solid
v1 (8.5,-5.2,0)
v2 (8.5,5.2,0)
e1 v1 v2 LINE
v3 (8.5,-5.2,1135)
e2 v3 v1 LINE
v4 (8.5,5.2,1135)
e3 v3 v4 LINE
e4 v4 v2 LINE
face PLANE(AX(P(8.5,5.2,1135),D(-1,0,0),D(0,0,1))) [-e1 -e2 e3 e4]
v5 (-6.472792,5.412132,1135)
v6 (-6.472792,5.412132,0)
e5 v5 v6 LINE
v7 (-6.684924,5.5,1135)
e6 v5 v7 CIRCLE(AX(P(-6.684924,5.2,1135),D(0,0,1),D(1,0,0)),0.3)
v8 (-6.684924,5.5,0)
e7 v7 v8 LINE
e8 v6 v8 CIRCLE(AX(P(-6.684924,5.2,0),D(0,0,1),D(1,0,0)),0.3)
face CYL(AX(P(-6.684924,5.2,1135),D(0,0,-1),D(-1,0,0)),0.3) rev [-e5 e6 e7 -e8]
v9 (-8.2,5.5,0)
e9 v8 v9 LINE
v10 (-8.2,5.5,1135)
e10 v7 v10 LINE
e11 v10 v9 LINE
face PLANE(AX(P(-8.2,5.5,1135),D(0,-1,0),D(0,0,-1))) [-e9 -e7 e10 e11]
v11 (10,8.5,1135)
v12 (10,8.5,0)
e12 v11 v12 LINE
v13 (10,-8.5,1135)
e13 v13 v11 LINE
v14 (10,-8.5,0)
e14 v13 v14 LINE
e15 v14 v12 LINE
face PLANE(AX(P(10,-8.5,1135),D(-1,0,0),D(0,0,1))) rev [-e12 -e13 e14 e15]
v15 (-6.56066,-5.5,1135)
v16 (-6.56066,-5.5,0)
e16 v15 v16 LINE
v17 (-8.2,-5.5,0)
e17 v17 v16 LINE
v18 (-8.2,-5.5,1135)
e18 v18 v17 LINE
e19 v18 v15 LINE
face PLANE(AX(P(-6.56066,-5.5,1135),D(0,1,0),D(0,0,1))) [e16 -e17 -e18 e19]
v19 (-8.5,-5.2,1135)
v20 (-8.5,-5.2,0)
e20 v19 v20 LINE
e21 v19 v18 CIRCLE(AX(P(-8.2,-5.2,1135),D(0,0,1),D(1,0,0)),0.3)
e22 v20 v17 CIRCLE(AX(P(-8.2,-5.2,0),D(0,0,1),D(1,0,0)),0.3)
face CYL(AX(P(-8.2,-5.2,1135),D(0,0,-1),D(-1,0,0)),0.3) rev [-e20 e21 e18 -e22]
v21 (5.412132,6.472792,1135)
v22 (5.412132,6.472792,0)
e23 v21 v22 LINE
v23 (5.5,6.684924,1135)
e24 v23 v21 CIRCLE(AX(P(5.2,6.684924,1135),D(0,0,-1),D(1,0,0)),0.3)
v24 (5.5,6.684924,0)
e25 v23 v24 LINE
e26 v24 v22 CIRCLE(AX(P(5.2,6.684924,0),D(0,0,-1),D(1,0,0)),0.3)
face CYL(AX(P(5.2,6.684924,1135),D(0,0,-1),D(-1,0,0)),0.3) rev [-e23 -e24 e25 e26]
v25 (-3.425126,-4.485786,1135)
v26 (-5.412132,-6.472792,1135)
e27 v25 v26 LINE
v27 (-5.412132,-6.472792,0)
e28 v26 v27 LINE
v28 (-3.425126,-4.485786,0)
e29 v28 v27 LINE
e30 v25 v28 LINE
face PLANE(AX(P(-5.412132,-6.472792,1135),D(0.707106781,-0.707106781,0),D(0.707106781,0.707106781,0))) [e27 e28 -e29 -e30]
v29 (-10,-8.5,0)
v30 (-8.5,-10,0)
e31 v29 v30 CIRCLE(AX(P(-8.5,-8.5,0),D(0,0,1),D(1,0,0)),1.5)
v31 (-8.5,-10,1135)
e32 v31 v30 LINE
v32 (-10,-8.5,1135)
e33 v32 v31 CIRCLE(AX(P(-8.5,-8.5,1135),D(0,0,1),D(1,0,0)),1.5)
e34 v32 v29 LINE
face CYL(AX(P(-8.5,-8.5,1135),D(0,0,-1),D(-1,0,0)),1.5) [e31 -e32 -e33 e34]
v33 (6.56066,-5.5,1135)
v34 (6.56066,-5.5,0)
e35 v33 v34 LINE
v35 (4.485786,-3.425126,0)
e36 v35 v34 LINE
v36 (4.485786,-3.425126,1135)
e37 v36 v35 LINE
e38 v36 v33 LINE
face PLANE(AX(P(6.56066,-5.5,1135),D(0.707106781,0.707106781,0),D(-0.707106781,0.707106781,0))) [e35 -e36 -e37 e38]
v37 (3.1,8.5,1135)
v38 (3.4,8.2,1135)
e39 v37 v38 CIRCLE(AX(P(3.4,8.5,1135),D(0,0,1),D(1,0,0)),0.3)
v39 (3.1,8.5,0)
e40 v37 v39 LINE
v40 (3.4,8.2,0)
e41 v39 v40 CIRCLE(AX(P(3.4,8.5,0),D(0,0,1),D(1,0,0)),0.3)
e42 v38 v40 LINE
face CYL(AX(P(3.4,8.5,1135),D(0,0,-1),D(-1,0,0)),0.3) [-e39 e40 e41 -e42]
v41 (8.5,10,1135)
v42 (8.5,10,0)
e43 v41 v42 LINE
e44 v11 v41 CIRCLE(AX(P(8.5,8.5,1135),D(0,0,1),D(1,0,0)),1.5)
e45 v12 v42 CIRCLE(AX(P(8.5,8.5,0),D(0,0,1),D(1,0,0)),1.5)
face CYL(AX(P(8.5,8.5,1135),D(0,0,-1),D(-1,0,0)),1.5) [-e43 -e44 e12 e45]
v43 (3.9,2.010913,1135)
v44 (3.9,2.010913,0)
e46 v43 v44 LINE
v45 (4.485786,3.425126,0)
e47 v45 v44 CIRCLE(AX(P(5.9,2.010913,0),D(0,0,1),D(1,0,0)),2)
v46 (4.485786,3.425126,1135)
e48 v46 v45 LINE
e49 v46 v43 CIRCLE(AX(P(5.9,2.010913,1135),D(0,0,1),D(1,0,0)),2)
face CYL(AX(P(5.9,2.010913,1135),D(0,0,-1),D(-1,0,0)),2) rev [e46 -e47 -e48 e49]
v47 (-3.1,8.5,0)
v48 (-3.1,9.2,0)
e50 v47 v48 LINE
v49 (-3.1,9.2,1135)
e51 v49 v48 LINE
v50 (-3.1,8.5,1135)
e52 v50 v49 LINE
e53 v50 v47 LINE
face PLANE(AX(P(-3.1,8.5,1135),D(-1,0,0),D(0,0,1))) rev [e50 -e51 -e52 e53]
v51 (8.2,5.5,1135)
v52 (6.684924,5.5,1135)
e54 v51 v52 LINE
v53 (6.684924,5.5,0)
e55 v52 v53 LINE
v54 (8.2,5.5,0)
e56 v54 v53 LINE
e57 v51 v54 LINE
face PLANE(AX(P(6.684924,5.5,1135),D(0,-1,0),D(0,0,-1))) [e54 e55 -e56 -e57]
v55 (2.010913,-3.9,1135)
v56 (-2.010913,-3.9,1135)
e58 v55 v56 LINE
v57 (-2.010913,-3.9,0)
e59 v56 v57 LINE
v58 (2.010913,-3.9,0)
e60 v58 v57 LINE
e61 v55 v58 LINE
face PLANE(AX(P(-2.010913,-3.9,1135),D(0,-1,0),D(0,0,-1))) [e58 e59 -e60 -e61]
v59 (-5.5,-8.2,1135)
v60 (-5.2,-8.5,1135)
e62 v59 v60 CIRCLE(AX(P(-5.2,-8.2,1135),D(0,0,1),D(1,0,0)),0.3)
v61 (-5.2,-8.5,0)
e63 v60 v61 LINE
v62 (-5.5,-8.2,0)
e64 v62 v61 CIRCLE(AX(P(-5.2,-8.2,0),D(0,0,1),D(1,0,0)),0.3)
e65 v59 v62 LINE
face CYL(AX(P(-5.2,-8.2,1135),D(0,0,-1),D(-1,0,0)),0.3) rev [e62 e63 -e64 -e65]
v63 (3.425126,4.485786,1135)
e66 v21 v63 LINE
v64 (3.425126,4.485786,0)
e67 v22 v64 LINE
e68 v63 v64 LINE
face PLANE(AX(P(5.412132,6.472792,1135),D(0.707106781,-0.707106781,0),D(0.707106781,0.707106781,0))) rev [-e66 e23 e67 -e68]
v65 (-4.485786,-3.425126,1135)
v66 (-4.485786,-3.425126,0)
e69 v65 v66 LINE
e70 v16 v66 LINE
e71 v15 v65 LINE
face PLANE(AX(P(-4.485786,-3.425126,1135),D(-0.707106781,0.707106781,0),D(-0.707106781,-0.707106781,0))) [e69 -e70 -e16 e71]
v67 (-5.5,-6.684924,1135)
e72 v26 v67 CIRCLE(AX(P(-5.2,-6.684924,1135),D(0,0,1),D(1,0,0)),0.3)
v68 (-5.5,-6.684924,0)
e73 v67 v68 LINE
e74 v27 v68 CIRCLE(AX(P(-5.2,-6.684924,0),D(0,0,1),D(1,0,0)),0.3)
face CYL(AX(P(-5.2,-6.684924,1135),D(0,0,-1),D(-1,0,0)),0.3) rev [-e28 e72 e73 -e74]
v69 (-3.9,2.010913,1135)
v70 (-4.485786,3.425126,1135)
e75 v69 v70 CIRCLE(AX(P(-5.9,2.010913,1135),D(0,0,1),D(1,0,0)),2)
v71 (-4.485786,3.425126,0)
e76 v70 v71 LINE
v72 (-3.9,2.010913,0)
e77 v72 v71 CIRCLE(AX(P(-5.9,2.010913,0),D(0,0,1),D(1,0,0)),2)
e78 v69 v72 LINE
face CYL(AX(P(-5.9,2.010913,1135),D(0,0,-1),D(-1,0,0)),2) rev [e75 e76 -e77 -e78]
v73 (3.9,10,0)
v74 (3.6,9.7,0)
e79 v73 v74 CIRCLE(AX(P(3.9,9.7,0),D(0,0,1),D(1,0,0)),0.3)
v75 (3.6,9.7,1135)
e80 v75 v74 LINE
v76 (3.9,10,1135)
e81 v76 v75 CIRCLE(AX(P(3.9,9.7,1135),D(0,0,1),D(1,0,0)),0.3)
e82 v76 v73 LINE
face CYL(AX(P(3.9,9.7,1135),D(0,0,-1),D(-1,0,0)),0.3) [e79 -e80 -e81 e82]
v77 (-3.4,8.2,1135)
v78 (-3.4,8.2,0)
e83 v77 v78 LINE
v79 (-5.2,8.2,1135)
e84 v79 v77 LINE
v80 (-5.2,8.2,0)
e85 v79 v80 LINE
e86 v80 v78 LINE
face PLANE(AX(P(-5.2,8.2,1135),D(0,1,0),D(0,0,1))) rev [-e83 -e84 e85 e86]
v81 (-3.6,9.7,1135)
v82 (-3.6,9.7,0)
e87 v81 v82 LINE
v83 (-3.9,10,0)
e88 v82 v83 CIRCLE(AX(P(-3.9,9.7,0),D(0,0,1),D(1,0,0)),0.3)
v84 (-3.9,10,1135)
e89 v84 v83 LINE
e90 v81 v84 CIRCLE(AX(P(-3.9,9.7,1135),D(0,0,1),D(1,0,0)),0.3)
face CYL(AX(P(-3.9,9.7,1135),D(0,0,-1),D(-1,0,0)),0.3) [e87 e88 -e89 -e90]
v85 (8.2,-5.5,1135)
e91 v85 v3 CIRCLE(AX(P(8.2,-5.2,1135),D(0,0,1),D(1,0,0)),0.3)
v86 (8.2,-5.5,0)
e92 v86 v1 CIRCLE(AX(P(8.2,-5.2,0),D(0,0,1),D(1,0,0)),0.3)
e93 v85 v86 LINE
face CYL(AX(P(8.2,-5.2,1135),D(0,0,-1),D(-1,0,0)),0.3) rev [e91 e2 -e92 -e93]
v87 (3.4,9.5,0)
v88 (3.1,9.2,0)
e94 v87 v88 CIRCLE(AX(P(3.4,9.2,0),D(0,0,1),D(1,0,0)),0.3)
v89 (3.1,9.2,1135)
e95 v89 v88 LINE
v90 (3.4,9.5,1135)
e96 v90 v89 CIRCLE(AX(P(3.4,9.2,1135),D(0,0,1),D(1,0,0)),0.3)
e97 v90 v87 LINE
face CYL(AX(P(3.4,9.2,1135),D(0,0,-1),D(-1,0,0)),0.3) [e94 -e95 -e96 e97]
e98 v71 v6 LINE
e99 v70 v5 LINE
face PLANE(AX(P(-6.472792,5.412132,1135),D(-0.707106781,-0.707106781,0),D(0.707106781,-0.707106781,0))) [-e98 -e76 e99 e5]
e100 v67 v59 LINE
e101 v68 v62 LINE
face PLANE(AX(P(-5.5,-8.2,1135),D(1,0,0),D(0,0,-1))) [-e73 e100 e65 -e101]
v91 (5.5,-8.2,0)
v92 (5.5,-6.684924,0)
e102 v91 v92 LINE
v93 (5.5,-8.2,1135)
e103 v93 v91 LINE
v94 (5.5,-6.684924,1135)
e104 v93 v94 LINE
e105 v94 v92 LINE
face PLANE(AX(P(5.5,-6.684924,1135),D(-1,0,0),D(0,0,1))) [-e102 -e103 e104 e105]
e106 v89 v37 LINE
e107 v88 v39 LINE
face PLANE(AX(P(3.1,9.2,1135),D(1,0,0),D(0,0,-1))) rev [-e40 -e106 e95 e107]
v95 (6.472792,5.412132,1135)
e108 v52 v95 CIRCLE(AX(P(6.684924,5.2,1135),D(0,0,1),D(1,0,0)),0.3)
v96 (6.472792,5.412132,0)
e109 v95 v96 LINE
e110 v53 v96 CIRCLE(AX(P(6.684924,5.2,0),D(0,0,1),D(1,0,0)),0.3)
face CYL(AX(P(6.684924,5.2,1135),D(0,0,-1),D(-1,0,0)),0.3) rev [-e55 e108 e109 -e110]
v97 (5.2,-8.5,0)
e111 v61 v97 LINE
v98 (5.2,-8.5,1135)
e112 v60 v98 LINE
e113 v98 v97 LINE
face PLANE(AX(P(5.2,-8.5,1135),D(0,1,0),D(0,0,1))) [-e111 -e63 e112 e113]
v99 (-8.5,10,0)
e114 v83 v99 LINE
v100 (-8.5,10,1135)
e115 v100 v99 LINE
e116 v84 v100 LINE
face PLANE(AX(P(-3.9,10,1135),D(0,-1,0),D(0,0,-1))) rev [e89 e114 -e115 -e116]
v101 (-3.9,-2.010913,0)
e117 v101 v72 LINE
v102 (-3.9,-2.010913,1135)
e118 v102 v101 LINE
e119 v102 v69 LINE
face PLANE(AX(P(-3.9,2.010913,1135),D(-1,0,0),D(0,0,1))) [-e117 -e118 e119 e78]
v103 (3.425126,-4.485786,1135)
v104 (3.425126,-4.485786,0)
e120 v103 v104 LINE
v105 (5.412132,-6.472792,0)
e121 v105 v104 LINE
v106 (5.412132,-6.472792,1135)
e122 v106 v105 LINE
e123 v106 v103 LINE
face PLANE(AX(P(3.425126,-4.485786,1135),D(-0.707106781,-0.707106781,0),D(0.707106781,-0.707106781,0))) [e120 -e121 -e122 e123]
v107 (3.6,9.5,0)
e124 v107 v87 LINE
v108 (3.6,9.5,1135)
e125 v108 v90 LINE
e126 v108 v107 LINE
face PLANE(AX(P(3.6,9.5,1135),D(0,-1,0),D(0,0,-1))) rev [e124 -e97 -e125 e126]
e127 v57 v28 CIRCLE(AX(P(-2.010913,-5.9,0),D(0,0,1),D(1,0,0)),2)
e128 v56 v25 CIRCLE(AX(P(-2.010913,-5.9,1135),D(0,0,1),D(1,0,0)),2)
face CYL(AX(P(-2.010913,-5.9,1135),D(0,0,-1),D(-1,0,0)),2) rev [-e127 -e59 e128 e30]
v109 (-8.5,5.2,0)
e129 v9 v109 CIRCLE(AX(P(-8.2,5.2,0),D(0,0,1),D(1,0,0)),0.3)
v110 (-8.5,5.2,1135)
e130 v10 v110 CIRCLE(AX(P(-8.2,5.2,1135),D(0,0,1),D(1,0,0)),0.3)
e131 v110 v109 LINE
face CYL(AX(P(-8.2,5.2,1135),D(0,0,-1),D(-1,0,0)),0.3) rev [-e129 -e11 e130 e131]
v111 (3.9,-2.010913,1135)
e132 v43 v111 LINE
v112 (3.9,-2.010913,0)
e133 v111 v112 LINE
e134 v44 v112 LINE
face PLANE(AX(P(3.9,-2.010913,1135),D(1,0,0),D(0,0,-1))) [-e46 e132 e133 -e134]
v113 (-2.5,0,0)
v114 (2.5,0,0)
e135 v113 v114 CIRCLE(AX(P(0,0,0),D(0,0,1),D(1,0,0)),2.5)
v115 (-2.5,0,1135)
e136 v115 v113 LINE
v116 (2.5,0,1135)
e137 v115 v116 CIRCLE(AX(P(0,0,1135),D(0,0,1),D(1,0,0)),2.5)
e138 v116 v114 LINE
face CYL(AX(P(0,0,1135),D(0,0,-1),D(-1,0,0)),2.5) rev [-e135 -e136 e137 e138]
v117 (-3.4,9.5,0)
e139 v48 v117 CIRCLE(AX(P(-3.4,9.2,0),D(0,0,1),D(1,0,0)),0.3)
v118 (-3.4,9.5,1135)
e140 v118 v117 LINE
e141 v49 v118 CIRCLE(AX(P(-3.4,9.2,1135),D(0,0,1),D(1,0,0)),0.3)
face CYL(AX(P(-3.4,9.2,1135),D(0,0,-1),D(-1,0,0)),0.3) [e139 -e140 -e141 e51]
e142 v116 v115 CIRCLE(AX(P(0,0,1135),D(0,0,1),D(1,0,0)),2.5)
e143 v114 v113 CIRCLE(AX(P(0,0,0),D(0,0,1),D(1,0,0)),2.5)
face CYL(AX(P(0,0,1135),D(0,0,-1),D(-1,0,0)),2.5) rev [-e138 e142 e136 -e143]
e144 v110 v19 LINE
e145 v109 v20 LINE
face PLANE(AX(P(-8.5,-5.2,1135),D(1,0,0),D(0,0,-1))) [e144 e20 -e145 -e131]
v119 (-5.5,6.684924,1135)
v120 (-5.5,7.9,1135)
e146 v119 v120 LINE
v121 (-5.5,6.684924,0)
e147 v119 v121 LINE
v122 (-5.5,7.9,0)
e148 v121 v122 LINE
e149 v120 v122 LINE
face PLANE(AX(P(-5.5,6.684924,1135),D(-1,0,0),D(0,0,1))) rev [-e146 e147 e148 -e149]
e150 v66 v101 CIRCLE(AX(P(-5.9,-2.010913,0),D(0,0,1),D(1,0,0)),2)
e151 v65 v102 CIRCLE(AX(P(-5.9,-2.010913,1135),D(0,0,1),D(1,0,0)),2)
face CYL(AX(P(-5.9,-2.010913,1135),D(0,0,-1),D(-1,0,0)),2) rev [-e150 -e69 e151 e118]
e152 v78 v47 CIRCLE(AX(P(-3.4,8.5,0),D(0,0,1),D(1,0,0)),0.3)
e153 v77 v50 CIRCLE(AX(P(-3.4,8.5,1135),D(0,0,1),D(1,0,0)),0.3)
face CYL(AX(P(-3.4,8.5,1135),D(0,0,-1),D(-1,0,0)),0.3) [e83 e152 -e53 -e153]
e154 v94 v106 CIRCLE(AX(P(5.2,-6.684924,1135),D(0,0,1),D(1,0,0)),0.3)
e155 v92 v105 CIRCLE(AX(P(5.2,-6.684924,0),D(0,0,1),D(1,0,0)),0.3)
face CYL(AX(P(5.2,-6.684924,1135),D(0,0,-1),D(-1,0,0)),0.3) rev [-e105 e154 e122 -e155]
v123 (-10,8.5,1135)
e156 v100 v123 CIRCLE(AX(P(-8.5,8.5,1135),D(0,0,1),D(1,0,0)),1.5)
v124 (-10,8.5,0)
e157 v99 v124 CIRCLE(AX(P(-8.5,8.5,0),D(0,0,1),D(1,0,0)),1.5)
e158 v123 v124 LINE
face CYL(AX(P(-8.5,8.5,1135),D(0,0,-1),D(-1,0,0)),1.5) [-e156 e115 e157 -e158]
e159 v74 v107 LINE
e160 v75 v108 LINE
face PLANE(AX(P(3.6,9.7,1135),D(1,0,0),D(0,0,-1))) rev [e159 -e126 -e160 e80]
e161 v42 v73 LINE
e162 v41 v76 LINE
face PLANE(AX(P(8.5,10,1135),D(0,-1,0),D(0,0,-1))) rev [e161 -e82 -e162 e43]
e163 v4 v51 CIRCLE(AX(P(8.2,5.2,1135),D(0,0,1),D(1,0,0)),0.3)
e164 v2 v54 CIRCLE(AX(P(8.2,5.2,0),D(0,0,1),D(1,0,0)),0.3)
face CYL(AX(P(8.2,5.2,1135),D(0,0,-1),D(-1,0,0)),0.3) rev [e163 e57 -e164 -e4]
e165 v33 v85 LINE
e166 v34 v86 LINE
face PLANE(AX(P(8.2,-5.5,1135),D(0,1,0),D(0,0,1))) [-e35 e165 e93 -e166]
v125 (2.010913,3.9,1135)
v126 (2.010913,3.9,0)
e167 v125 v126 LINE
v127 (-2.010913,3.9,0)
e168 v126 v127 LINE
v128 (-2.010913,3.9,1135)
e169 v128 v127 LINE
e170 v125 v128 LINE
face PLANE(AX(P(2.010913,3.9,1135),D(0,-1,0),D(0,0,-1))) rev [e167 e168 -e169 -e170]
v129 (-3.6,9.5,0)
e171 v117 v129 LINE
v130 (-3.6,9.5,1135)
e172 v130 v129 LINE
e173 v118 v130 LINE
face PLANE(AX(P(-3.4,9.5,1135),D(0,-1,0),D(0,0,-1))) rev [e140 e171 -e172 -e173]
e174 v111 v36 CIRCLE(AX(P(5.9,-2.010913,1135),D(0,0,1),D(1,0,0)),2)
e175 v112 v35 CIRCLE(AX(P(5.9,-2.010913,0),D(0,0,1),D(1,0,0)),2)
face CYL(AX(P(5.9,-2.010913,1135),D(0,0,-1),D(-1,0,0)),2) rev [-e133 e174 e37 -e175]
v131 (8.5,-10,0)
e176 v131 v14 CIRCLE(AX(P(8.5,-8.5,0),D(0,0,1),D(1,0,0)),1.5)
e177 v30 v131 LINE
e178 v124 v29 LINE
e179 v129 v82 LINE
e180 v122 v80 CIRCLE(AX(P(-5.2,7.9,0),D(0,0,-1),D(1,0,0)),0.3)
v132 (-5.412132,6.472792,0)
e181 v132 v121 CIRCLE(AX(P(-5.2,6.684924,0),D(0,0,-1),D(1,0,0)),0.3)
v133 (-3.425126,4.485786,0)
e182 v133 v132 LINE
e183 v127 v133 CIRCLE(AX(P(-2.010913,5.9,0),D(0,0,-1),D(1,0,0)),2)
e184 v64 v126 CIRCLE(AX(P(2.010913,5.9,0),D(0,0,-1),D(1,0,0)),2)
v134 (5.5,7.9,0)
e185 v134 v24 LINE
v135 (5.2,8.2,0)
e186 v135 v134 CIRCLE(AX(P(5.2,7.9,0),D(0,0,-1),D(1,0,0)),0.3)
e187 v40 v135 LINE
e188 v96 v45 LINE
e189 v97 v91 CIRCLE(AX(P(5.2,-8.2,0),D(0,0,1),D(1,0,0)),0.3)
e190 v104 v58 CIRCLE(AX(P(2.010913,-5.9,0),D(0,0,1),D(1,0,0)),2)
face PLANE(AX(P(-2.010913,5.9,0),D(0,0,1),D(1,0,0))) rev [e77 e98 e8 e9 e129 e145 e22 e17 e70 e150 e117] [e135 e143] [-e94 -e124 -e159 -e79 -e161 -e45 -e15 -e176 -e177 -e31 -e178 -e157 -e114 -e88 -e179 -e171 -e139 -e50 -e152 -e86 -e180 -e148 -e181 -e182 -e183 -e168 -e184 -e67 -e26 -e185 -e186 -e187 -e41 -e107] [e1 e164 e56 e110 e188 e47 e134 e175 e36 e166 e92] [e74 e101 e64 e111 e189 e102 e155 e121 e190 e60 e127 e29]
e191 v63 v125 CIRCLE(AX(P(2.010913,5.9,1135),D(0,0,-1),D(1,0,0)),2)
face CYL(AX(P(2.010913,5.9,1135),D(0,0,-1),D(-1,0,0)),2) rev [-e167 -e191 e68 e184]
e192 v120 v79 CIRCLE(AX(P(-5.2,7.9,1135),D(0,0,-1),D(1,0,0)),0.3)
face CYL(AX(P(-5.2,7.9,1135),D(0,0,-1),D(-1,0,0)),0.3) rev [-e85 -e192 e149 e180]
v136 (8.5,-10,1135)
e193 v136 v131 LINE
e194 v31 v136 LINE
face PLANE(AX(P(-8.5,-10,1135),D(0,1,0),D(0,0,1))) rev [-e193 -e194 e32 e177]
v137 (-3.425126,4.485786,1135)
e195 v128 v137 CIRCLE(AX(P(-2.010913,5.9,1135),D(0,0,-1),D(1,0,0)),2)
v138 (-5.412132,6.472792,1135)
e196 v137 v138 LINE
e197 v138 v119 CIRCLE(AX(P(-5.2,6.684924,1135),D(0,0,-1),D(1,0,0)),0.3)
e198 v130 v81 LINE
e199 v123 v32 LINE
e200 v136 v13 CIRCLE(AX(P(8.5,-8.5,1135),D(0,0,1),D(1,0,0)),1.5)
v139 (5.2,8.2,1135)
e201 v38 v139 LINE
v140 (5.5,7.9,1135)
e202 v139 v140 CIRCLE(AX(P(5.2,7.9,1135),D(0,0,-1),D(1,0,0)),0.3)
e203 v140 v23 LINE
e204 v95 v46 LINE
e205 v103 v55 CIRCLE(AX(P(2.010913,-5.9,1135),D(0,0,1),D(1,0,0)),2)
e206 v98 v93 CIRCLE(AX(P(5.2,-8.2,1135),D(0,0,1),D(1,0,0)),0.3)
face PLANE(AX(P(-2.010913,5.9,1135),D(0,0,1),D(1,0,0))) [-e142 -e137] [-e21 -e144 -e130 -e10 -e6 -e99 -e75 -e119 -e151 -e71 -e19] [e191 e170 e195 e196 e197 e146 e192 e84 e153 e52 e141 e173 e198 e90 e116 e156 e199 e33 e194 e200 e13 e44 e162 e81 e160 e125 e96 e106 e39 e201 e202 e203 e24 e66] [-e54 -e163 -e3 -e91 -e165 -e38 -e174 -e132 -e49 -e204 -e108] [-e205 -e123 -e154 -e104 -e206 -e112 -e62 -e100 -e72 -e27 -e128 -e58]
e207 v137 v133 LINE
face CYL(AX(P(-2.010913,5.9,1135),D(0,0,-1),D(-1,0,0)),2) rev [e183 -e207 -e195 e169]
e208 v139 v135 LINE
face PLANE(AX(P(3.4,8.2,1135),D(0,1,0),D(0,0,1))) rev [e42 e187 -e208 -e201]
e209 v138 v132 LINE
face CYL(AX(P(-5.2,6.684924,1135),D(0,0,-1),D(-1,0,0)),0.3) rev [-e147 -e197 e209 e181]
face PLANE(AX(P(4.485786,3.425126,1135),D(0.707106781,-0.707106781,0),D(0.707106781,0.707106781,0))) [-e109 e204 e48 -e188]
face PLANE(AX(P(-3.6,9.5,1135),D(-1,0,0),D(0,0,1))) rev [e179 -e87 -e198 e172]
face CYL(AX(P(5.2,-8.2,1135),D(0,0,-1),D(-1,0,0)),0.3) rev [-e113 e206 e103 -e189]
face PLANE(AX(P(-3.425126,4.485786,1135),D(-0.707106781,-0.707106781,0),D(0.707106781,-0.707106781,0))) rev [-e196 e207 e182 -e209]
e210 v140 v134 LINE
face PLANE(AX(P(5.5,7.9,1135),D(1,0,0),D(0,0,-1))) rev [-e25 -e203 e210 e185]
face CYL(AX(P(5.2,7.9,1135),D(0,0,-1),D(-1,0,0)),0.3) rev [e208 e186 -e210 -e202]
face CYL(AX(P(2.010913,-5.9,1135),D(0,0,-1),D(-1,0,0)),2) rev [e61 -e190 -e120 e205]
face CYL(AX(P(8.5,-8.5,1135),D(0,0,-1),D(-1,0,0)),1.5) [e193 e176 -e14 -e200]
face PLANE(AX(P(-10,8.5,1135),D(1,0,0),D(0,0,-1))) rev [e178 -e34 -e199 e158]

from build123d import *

# Parameters (mm, degrees)
SKETCH_1_R      = 2.5
EXTRUDE_1_DEPTH = 1135


with BuildPart() as part:
    # 草图1 → 凸台-拉伸1 (new body)
    with BuildSketch(Plane.XY):
        with BuildLine():
            Line((-3.425126266, 4.485786438), (-5.412132034, 6.472792206))
            ThreePointArc((-5.412132034, 6.472792206), (-5.47716386, 6.570119211), (-5.5, 6.68492424))
            Line((-5.5, 6.68492424), (-5.5, 7.9))
            ThreePointArc((-5.5, 7.9), (-5.412132034, 8.112132034), (-5.2, 8.2))
            Line((-5.2, 8.2), (-3.4, 8.2))
            ThreePointArc((-3.4, 8.2), (-3.187867966, 8.287867966), (-3.1, 8.5))
            Line((-3.1, 8.5), (-3.1, 9.2))
            ThreePointArc((-3.1, 9.2), (-3.187867966, 9.412132034), (-3.4, 9.5))
            Line((-3.4, 9.5), (-3.6, 9.5))
            Line((-3.6, 9.5), (-3.6, 9.7))
            ThreePointArc((-3.6, 9.7), (-3.687867966, 9.912132034), (-3.9, 10))
            Line((-3.9, 10), (-8.5, 10))
            ThreePointArc((-8.5, 10), (-9.560660172, 9.560660172), (-10, 8.5))
            Line((-10, 8.5), (-10, -8.5))
            ThreePointArc((-10, -8.5), (-9.560660172, -9.560660172), (-8.5, -10))
            Line((-8.5, -10), (8.5, -10))
            ThreePointArc((8.5, -10), (9.560660172, -9.560660172), (10, -8.5))
            Line((10, -8.5), (10, 8.5))
            ThreePointArc((10, 8.5), (9.560660172, 9.560660172), (8.5, 10))
            Line((8.5, 10), (3.9, 10))
            ThreePointArc((3.9, 10), (3.687867966, 9.912132034), (3.6, 9.7))
            Line((3.6, 9.7), (3.6, 9.5))
            Line((3.6, 9.5), (3.4, 9.5))
            ThreePointArc((3.4, 9.5), (3.187867966, 9.412132034), (3.1, 9.2))
            Line((3.1, 9.2), (3.1, 8.5))
            ThreePointArc((3.1, 8.5), (3.187867966, 8.287867966), (3.4, 8.2))
            Line((3.4, 8.2), (5.2, 8.2))
            ThreePointArc((5.2, 8.2), (5.412132034, 8.112132034), (5.5, 7.9))
            Line((5.5, 7.9), (5.5, 6.68492424))
            ThreePointArc((5.5, 6.68492424), (5.47716386, 6.570119211), (5.412132034, 6.472792206))
            Line((5.412132034, 6.472792206), (3.425126266, 4.485786438))
            ThreePointArc((3.425126266, 4.485786438), (2.776279568, 4.052240935), (2.010912703, 3.9))
            Line((2.010912703, 3.9), (-2.010912703, 3.9))
            ThreePointArc((-2.010912703, 3.9), (-2.776279568, 4.052240935), (-3.425126266, 4.485786438))
        make_face()
        Circle(SKETCH_1_R, mode=Mode.SUBTRACT)
        with BuildLine():
            Line((-3.9, 2.010912703), (-3.9, -2.010912703))
            ThreePointArc((-3.9, -2.010912703), (-4.052240935, -2.776279568), (-4.485786438, -3.425126266))
            Line((-4.485786438, -3.425126266), (-6.560660172, -5.5))
            Line((-6.560660172, -5.5), (-8.2, -5.5))
            ThreePointArc((-8.2, -5.5), (-8.412132034, -5.412132034), (-8.5, -5.2))
            Line((-8.5, -5.2), (-8.5, 5.2))
            ThreePointArc((-8.5, 5.2), (-8.412132034, 5.412132034), (-8.2, 5.5))
            Line((-8.2, 5.5), (-6.68492424, 5.5))
            ThreePointArc((-6.68492424, 5.5), (-6.570119211, 5.47716386), (-6.472792206, 5.412132034))
            Line((-6.472792206, 5.412132034), (-4.485786438, 3.425126266))
            ThreePointArc((-4.485786438, 3.425126266), (-4.052240935, 2.776279568), (-3.9, 2.010912703))
        make_face(mode=Mode.SUBTRACT)
        with BuildLine():
            Line((4.485786438, 3.425126266), (6.472792206, 5.412132034))
            ThreePointArc((6.472792206, 5.412132034), (6.570119211, 5.47716386), (6.68492424, 5.5))
            Line((6.68492424, 5.5), (8.2, 5.5))
            ThreePointArc((8.2, 5.5), (8.412132034, 5.412132034), (8.5, 5.2))
            Line((8.5, 5.2), (8.5, -5.2))
            ThreePointArc((8.5, -5.2), (8.412132034, -5.412132034), (8.2, -5.5))
            Line((8.2, -5.5), (6.560660172, -5.5))
            Line((6.560660172, -5.5), (4.485786438, -3.425126266))
            ThreePointArc((4.485786438, -3.425126266), (4.052240935, -2.776279568), (3.9, -2.010912703))
            Line((3.9, -2.010912703), (3.9, 2.010912703))
            ThreePointArc((3.9, 2.010912703), (4.052240935, 2.776279568), (4.485786438, 3.425126266))
        make_face(mode=Mode.SUBTRACT)
        with BuildLine():
            Line((-2.010912703, -3.9), (2.010912703, -3.9))
            ThreePointArc((2.010912703, -3.9), (2.776279568, -4.052240935), (3.425126266, -4.485786438))
            Line((3.425126266, -4.485786438), (5.412132034, -6.472792206))
            ThreePointArc((5.412132034, -6.472792206), (5.47716386, -6.570119211), (5.5, -6.68492424))
            Line((5.5, -6.68492424), (5.5, -8.2))
            ThreePointArc((5.5, -8.2), (5.412132034, -8.412132034), (5.2, -8.5))
            Line((5.2, -8.5), (-5.2, -8.5))
            ThreePointArc((-5.2, -8.5), (-5.412132034, -8.412132034), (-5.5, -8.2))
            Line((-5.5, -8.2), (-5.5, -6.68492424))
            ThreePointArc((-5.5, -6.68492424), (-5.47716386, -6.570119211), (-5.412132034, -6.472792206))
            Line((-5.412132034, -6.472792206), (-3.425126266, -4.485786438))
            ThreePointArc((-3.425126266, -4.485786438), (-2.776279568, -4.052240935), (-2.010912703, -3.9))
        make_face(mode=Mode.SUBTRACT)
    extrude(amount=EXTRUDE_1_DEPTH)


solid = part.part
